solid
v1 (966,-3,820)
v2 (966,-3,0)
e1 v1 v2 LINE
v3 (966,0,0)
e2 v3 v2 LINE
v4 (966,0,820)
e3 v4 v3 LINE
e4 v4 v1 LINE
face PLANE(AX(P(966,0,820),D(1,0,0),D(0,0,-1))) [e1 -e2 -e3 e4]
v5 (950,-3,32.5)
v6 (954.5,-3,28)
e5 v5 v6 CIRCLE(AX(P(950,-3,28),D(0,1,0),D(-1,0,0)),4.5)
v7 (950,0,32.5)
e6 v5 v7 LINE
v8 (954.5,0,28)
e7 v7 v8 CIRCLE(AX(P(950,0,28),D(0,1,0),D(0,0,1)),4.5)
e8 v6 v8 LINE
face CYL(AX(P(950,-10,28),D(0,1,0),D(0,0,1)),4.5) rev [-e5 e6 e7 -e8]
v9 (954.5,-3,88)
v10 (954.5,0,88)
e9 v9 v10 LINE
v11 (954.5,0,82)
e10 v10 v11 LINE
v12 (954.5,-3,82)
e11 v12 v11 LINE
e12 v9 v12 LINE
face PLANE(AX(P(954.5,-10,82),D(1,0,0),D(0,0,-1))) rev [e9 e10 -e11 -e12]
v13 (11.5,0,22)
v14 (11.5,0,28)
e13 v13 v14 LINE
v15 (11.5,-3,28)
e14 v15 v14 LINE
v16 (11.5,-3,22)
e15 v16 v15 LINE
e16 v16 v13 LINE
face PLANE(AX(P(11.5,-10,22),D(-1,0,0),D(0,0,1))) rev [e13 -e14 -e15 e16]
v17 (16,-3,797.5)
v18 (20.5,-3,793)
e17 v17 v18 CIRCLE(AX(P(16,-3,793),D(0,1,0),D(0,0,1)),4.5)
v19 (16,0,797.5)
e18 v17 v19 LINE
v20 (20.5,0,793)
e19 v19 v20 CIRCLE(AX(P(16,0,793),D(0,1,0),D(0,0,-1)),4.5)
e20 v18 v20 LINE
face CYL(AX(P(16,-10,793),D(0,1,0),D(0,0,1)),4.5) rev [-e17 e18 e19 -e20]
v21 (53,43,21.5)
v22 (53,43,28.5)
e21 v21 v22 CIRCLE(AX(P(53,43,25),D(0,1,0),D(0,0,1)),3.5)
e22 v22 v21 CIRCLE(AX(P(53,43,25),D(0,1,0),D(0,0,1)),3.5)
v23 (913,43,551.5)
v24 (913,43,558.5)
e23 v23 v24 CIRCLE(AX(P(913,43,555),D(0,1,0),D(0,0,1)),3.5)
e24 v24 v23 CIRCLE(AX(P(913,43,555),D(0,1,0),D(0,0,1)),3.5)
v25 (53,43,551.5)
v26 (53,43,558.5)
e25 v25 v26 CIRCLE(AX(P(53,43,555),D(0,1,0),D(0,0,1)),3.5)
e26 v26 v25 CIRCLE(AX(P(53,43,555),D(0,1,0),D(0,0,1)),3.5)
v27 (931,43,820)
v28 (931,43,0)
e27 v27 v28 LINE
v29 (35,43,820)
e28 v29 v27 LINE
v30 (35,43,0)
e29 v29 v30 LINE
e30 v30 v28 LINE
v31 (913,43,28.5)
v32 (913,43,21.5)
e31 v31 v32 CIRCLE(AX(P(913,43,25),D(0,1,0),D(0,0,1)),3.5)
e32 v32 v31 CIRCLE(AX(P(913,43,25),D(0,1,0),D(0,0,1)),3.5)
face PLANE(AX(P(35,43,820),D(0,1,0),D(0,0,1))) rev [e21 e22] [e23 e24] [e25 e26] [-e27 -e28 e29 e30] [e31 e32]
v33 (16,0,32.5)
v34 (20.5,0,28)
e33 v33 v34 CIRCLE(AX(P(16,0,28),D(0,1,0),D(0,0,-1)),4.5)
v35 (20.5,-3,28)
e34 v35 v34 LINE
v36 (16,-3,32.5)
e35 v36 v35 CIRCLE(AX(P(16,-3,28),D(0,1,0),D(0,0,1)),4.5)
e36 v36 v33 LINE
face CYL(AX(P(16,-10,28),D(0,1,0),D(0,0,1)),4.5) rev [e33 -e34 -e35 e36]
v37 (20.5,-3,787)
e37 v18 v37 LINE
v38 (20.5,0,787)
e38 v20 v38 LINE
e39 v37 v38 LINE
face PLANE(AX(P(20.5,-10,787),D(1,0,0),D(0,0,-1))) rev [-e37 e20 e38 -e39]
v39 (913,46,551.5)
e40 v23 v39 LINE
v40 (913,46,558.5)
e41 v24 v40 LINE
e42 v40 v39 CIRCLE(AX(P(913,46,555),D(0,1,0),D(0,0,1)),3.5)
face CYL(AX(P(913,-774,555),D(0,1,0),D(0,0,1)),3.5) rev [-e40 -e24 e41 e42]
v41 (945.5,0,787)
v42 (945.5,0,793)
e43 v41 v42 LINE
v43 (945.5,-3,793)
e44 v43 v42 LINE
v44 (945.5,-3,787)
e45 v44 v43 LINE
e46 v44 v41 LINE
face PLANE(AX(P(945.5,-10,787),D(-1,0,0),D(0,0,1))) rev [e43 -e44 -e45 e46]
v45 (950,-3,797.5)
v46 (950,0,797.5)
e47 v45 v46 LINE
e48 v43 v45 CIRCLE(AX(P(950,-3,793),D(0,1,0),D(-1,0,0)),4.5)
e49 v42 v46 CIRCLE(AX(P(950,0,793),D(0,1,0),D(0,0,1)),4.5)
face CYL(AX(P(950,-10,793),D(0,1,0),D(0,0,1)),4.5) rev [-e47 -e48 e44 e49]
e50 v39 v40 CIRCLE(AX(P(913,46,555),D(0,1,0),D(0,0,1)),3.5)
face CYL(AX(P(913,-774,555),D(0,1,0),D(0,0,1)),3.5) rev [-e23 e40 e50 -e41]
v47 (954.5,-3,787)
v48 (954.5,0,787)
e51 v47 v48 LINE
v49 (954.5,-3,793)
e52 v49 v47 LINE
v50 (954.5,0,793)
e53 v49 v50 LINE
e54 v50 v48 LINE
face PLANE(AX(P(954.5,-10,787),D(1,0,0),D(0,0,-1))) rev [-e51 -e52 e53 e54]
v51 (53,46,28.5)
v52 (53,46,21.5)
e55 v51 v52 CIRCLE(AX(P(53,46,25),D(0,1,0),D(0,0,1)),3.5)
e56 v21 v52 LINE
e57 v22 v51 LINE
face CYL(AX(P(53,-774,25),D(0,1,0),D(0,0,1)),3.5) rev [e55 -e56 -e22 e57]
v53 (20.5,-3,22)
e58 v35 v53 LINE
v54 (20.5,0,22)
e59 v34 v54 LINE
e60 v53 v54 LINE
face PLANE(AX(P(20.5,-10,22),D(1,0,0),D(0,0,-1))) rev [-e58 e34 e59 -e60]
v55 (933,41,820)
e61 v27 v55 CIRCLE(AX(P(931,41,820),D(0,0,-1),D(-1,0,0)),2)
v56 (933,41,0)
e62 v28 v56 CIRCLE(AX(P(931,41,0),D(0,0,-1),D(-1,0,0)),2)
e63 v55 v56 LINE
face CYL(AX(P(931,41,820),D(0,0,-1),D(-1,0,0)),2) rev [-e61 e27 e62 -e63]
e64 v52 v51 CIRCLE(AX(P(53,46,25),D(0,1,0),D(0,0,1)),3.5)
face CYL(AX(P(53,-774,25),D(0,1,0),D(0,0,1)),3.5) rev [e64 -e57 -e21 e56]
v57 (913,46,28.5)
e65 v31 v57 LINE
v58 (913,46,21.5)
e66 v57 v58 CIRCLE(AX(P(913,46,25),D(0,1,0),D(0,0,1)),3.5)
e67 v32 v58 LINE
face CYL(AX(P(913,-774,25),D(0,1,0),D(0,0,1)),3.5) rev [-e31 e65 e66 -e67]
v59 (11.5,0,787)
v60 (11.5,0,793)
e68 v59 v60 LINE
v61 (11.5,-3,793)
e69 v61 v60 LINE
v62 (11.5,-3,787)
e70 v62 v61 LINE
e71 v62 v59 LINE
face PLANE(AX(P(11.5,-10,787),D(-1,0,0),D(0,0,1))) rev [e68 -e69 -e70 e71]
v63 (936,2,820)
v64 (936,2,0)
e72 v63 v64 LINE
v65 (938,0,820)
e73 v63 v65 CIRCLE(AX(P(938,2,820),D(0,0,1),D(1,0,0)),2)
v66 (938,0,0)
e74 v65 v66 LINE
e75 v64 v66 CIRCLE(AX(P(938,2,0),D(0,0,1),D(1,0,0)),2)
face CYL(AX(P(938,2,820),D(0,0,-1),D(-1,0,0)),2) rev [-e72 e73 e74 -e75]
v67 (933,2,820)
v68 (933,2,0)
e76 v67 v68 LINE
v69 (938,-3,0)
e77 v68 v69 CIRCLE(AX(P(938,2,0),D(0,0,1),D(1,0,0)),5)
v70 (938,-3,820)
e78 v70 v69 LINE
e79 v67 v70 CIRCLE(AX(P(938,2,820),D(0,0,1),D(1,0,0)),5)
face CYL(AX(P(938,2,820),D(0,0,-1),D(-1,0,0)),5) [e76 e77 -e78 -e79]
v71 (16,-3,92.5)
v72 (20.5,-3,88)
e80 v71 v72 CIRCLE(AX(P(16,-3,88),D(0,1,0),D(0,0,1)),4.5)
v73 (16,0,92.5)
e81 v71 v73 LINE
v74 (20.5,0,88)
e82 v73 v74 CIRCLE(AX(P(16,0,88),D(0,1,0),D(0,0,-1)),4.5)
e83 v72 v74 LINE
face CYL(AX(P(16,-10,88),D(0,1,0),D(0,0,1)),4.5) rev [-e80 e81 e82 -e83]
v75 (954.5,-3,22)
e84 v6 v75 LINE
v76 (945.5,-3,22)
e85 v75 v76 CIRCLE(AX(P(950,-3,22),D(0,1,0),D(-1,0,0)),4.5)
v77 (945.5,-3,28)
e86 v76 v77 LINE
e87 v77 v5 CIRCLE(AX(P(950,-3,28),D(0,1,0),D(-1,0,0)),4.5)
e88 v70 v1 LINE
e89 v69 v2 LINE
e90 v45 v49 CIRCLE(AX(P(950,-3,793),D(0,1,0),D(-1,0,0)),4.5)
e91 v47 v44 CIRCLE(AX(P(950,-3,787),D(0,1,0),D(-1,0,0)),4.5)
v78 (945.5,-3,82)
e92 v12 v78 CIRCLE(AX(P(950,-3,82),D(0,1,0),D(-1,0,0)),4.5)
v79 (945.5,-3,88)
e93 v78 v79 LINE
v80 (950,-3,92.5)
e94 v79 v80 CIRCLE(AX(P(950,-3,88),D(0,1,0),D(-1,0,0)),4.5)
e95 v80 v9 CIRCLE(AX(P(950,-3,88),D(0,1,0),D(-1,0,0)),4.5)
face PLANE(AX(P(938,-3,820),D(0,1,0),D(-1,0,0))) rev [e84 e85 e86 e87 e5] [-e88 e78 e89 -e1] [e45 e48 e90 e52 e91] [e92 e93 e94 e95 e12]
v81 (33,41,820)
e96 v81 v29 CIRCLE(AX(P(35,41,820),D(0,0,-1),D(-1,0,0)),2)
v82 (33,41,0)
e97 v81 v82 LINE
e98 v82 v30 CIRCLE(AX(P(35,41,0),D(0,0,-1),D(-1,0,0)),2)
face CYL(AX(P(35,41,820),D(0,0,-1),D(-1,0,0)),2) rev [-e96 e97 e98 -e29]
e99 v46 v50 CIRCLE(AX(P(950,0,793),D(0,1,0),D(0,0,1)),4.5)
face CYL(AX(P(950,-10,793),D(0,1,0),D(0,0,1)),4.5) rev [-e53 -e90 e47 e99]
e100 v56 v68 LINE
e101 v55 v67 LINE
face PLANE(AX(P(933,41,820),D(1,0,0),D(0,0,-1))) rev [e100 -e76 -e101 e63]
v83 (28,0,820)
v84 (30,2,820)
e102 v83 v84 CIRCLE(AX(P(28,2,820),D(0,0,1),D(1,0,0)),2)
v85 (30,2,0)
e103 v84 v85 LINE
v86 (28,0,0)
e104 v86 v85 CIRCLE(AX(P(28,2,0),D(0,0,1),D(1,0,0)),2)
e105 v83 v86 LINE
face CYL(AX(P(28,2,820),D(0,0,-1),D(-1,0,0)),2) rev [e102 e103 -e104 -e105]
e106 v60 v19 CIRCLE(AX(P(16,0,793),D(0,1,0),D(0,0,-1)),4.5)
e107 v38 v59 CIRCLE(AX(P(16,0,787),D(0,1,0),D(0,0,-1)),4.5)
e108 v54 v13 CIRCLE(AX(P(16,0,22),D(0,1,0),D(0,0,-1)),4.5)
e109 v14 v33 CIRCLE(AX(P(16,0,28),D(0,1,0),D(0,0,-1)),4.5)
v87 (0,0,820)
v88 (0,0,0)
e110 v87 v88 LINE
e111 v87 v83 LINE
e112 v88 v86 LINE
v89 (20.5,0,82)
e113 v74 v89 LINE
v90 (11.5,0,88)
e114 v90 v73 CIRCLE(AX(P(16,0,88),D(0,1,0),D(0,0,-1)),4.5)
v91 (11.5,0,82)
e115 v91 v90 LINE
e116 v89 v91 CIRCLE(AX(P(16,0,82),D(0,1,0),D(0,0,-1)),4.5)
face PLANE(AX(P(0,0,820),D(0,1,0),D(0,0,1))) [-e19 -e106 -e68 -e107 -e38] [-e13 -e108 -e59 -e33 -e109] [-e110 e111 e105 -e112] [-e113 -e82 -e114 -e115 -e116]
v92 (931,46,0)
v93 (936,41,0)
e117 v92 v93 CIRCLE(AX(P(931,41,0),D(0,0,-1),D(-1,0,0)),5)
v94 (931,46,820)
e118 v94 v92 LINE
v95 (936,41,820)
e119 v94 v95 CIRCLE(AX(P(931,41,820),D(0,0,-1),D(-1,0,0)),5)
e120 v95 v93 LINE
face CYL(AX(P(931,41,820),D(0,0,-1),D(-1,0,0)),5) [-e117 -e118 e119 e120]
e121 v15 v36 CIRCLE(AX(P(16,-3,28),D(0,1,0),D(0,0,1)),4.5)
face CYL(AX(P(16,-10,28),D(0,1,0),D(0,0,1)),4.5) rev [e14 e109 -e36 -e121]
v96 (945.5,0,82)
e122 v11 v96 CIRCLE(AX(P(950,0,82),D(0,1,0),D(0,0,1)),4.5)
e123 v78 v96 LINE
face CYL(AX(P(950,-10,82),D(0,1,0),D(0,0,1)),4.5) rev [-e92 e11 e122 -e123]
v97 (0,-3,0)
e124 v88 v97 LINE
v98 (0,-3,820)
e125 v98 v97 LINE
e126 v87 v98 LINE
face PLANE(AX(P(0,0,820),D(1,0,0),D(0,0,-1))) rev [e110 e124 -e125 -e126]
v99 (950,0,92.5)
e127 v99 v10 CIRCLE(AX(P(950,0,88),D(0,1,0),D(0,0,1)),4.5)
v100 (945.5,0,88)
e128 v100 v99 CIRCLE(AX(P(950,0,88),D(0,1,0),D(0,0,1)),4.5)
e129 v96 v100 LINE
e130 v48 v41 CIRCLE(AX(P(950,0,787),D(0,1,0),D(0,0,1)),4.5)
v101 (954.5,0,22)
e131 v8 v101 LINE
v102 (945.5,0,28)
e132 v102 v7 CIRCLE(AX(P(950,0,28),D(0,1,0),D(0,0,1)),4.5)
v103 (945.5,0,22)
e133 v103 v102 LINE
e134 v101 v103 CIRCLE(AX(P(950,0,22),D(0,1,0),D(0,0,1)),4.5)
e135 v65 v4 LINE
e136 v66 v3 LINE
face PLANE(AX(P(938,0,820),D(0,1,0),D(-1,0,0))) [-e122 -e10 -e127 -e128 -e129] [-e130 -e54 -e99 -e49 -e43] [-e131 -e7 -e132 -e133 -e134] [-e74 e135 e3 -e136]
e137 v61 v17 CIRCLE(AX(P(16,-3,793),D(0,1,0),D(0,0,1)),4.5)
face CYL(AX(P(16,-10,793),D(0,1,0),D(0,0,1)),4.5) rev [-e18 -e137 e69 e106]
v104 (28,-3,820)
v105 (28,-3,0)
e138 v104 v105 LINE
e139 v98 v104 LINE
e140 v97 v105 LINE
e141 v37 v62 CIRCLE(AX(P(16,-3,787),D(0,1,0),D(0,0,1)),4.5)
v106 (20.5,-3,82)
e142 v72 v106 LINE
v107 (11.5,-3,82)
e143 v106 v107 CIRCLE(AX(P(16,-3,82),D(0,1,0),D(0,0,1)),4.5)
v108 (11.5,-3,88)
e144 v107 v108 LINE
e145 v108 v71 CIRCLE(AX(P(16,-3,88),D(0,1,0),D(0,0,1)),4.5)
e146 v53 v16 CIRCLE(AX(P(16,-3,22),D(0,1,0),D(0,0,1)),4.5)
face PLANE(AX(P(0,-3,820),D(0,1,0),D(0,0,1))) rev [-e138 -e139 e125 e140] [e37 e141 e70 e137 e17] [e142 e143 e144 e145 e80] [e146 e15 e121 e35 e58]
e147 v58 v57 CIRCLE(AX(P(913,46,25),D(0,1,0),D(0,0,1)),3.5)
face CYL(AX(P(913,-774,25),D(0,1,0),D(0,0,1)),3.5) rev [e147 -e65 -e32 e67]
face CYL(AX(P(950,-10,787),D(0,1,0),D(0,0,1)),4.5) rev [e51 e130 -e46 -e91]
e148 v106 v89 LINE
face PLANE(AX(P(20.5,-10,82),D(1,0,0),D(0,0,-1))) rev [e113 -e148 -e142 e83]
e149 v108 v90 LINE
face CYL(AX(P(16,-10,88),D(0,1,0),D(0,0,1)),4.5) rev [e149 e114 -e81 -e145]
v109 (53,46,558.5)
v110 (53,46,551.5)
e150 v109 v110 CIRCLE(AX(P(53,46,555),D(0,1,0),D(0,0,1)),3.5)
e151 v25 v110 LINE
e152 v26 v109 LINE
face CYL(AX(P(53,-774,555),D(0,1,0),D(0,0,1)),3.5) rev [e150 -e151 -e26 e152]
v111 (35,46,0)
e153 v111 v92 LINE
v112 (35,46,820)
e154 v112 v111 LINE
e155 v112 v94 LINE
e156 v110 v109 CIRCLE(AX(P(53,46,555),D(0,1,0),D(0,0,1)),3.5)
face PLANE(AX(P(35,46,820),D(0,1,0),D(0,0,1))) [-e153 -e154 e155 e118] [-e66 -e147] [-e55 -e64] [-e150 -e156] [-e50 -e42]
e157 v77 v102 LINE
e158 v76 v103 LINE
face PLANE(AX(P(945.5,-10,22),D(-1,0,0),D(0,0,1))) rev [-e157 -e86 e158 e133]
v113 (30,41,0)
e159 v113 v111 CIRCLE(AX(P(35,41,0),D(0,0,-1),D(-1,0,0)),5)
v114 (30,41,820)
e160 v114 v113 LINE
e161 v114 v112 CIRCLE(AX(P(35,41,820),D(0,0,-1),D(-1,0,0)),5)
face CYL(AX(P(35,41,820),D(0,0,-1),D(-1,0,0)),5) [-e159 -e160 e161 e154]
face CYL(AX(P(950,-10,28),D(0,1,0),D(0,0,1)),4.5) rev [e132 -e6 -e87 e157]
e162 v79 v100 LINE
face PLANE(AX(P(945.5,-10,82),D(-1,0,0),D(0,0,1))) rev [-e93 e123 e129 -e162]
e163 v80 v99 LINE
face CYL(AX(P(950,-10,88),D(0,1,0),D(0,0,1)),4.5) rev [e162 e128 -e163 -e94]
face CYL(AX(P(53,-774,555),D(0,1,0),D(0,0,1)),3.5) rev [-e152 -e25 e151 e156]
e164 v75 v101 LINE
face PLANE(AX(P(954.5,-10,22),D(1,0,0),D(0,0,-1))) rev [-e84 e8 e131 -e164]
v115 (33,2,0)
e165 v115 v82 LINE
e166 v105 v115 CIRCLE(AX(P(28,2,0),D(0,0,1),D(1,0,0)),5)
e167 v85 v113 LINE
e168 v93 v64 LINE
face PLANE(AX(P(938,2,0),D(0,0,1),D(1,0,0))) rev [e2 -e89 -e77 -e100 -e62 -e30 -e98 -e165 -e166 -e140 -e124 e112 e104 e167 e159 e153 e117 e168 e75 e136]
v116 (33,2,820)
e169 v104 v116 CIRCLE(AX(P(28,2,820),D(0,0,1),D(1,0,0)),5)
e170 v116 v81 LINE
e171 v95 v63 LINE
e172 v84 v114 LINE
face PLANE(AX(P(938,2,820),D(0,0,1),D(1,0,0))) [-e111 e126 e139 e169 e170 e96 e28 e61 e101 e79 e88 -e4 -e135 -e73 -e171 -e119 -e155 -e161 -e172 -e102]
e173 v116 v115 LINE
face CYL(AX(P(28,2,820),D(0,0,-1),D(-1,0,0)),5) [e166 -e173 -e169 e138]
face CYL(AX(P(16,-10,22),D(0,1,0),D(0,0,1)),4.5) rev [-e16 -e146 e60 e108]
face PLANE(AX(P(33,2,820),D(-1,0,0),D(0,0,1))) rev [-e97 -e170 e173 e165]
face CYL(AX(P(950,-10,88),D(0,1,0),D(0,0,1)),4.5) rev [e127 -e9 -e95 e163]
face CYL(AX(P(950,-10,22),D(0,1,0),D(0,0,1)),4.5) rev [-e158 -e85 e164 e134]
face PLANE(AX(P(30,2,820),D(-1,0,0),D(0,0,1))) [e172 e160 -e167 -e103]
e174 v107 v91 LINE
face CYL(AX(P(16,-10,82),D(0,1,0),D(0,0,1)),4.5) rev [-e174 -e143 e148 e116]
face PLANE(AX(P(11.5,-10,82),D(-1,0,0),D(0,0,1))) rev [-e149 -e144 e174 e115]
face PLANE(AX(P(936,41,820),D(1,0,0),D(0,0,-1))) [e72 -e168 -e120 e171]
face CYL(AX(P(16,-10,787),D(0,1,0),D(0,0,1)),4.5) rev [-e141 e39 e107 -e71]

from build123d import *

# Parameters (mm, degrees)
EXTRUDE_1_DEPTH     = 820
SKETCH_2_R          = 3.5
CUT_EXTRUDE_1_DEPTH = 820
CUT_EXTRUDE_2_DEPTH = 10


with BuildPart() as part:
    # 草图1 → 凸台-拉伸1 (new body)
    with BuildSketch(Plane.XY):
        with BuildLine():
            Line((0, 0), (28, 0))
            ThreePointArc((28, 0), (29.414213562, 0.585786438), (30, 2))
            Line((30, 2), (30, 41))
            ThreePointArc((30, 41), (31.464466094, 44.535533906), (35, 46))
            Line((35, 46), (931, 46))
            ThreePointArc((931, 46), (934.535533906, 44.535533906), (936, 41))
            Line((936, 41), (936, 2))
            ThreePointArc((936, 2), (936.585786438, 0.585786438), (938, 0))
            Line((938, 0), (966, 0))
            Line((966, 0), (966, -3))
            Line((966, -3), (938, -3))
            ThreePointArc((938, -3), (934.464466094, -1.535533906), (933, 2))
            Line((933, 2), (933, 41))
            ThreePointArc((933, 41), (932.414213562, 42.414213562), (931, 43))
            Line((931, 43), (35, 43))
            ThreePointArc((35, 43), (33.585786438, 42.414213562), (33, 41))
            Line((33, 41), (33, 2))
            ThreePointArc((33, 2), (31.535533906, -1.535533906), (28, -3))
            Line((28, -3), (0, -3))
            Line((0, -3), (0, 0))
        make_face()
    extrude(amount=EXTRUDE_1_DEPTH)

    # 草图2 → 切除-拉伸1 (cut)
    with BuildSketch(Plane(origin=(0, 46, 0), x_dir=(1, 0, 0), z_dir=(0, 1, 0))):
        with Locations(Location((53, -555, 0), (0, 0, 270))):
            Circle(SKETCH_2_R)
        with Locations(Location((53, -25, 0), (0, 0, 270))):
            Circle(SKETCH_2_R)
        with Locations(Location((913, -25, 0), (0, 0, 270))):
            Circle(SKETCH_2_R)
        with Locations(Location((913, -555, 0), (0, 0, 270))):
            Circle(SKETCH_2_R)
    extrude(amount=-CUT_EXTRUDE_1_DEPTH, mode=Mode.SUBTRACT)

    # 草图3 → 切除-拉伸2 (cut)
    with BuildSketch(Plane(origin=(0, 0, 0), x_dir=(1, 0, 0), z_dir=(0, 1, 0))):
        with BuildLine():
            Line((954.5, -82), (954.5, -88))
            ThreePointArc((954.5, -88), (950, -92.5), (945.5, -88))
            Line((945.5, -88), (945.5, -82))
            ThreePointArc((945.5, -82), (950, -77.5), (954.5, -82))
        make_face()
        with BuildLine():
            Line((954.5, -22), (954.5, -28))
            ThreePointArc((954.5, -28), (950, -32.5), (945.5, -28))
            Line((945.5, -28), (945.5, -22))
            ThreePointArc((945.5, -22), (950, -17.5), (954.5, -22))
        make_face()
        with BuildLine():
            Line((11.5, -82), (11.5, -88))
            ThreePointArc((11.5, -88), (16, -92.5), (20.5, -88))
            Line((20.5, -88), (20.5, -82))
            ThreePointArc((20.5, -82), (16, -77.5), (11.5, -82))
        make_face()
        with BuildLine():
            Line((11.5, -22), (11.5, -28))
            ThreePointArc((11.5, -28), (16, -32.5), (20.5, -28))
            Line((20.5, -28), (20.5, -22))
            ThreePointArc((20.5, -22), (16, -17.5), (11.5, -22))
        make_face()
        with BuildLine():
            Line((954.5, -787), (954.5, -793))
            ThreePointArc((954.5, -793), (950, -797.5), (945.5, -793))
            Line((945.5, -793), (945.5, -787))
            ThreePointArc((945.5, -787), (950, -782.5), (954.5, -787))
        make_face()
        with BuildLine():
            Line((11.5, -787), (11.5, -793))
            ThreePointArc((11.5, -793), (16, -797.5), (20.5, -793))
            Line((20.5, -793), (20.5, -787))
            ThreePointArc((20.5, -787), (16, -782.5), (11.5, -787))
        make_face()
    extrude(amount=-CUT_EXTRUDE_2_DEPTH, mode=Mode.SUBTRACT)


solid = part.part
